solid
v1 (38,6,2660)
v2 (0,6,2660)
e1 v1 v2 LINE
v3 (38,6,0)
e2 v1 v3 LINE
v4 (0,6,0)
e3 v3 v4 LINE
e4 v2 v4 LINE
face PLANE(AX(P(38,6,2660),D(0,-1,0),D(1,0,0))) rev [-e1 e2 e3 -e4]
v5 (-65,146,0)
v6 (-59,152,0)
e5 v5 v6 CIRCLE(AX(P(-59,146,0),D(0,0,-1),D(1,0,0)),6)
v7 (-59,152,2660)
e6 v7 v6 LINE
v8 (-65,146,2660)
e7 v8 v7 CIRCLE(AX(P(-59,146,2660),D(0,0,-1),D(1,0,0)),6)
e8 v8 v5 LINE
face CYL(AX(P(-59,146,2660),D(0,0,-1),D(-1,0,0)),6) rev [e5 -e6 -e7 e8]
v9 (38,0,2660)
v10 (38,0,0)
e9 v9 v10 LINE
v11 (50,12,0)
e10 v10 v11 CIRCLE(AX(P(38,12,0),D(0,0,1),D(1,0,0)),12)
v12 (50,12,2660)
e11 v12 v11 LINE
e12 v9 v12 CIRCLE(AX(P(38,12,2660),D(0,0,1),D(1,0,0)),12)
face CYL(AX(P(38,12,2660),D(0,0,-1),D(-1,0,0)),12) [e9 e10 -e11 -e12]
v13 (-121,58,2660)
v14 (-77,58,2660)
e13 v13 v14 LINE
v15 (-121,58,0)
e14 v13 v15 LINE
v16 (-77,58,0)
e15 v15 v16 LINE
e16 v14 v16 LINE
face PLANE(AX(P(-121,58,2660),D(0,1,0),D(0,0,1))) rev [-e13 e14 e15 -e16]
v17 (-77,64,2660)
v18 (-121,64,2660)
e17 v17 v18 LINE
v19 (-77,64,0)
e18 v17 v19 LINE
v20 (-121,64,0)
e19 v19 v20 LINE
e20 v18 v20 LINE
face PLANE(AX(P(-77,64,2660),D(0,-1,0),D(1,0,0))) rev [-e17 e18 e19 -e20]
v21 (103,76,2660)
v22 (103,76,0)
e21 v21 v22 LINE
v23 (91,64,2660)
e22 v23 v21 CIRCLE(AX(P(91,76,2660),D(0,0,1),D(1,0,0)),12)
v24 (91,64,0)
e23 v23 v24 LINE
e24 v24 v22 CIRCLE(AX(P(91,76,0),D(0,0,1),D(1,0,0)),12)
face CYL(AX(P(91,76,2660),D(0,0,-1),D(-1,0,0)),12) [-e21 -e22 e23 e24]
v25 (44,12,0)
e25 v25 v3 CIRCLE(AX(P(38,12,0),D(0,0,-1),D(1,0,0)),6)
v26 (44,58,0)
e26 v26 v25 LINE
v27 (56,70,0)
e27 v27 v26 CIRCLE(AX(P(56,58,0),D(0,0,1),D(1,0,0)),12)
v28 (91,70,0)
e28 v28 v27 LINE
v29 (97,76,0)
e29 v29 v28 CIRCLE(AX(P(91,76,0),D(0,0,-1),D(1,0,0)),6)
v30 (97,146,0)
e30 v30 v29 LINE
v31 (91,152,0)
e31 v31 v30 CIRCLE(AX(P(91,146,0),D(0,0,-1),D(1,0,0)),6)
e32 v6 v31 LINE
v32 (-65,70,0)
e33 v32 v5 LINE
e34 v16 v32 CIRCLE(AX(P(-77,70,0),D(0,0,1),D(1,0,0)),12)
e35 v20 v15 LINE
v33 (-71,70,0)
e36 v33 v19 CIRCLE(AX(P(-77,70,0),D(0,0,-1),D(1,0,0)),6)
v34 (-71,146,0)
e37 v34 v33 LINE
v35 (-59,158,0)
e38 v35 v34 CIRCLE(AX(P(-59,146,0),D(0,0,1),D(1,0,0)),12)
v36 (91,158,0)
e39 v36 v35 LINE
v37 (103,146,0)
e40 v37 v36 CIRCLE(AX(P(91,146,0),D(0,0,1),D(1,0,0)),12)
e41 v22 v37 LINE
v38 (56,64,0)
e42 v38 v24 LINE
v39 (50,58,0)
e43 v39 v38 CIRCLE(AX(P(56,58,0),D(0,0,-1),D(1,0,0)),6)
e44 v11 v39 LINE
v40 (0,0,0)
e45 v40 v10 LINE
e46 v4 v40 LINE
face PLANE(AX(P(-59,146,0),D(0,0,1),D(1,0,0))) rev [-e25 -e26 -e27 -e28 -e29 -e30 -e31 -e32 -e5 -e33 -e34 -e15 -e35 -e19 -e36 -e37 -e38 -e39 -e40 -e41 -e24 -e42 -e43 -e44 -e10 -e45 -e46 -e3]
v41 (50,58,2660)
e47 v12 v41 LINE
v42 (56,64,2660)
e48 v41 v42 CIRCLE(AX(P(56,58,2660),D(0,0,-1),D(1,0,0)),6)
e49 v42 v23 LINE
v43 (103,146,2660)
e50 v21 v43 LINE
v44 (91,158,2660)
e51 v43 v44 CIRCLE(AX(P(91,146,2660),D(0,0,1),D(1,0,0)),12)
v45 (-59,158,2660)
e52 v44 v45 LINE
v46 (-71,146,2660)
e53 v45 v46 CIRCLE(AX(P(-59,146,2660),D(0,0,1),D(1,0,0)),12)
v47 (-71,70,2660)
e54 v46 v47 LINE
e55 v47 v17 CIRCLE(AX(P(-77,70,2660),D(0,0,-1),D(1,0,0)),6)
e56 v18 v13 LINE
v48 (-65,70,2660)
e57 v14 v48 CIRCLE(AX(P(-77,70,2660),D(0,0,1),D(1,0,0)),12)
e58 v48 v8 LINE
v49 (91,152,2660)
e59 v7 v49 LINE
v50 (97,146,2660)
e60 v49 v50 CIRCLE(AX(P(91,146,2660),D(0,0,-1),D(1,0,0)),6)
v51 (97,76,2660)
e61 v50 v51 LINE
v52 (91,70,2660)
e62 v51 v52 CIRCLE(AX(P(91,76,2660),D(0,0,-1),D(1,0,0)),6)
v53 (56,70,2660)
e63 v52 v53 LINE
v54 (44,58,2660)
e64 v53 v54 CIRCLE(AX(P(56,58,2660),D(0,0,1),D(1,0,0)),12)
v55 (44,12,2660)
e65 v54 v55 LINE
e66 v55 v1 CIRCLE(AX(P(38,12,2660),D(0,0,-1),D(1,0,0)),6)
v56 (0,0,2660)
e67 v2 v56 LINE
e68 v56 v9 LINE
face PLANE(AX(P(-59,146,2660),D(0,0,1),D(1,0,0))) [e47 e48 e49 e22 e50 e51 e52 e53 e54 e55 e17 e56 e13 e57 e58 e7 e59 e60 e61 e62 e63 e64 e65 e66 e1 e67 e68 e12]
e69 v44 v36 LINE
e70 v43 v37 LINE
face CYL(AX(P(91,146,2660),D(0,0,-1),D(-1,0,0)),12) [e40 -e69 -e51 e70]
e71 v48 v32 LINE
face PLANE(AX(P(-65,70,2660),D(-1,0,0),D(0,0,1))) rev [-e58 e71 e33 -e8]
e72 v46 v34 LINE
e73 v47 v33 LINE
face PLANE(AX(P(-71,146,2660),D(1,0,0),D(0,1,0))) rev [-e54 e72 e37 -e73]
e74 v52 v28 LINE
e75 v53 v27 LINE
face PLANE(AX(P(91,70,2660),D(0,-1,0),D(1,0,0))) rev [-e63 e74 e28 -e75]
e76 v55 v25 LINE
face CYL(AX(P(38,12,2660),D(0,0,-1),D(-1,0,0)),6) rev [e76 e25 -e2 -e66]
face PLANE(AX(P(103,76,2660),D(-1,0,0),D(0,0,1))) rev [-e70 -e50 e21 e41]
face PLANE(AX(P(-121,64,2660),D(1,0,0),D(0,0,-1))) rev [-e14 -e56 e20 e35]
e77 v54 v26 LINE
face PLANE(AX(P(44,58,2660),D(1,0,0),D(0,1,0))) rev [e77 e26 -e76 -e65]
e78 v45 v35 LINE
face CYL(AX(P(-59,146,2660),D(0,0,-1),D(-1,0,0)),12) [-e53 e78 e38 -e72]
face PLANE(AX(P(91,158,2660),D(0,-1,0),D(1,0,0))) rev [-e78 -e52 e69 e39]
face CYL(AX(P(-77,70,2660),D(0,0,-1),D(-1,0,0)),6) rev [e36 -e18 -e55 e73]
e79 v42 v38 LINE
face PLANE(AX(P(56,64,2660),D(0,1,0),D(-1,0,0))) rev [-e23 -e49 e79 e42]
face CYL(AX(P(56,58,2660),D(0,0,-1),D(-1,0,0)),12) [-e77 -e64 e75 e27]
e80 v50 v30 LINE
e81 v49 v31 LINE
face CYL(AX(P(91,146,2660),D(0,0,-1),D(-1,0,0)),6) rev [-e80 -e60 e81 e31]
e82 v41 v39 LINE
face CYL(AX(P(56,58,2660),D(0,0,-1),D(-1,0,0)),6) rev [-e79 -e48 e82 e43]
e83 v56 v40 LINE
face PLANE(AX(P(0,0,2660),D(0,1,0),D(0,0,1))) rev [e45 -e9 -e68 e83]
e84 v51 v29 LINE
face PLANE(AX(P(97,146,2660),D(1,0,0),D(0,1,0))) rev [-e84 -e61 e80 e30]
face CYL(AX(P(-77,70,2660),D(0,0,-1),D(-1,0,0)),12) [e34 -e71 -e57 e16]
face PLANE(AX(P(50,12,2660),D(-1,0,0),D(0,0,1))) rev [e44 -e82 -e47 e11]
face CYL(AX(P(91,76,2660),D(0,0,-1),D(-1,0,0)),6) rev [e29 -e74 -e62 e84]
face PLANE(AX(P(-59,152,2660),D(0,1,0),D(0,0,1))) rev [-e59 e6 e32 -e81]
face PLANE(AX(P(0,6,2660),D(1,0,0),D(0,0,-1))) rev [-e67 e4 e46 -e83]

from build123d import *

# Parameters (mm, degrees)
BOSS_EXTRUDE1_DEPTH = 2660


with BuildPart() as part:
    # Sketch1 → Boss-Extrude1 (new body)
    with BuildSketch(Plane.XY):
        with BuildLine():
            Line((-70.999999998, 146), (-70.999999998, 70))
            ThreePointArc((-70.999999998, 70), (-72.757359311, 65.757359313), (-76.999999998, 64))
            Line((-76.999999998, 64), (-120.999999998, 64))
            Line((-120.999999998, 64), (-120.999999998, 58))
            Line((-120.999999998, 58), (-76.999999998, 58))
            ThreePointArc((-76.999999998, 58), (-68.514718624, 61.514718626), (-64.999999998, 70))
            Line((-64.999999998, 70), (-64.999999998, 146))
            ThreePointArc((-64.999999998, 146), (-63.242640685, 150.242640687), (-58.999999998, 152))
            Line((-58.999999998, 152), (91, 152))
            ThreePointArc((91, 152), (95.242640687, 150.242640687), (97, 146))
            Line((97, 146), (97, 76))
            ThreePointArc((97, 76), (95.242640687, 71.757359313), (91, 70))
            Line((91, 70), (56, 70))
            ThreePointArc((56, 70), (47.514718626, 66.485281374), (44, 58))
            Line((44, 58), (44, 12))
            ThreePointArc((44, 12), (42.242640687, 7.757359313), (38, 6))
            Line((38, 6), (0, 6))
            Line((0, 6), (0, 0))
            Line((0, 0), (38, 0))
            ThreePointArc((38, 0), (46.485281374, 3.514718626), (50, 12))
            Line((50, 12), (50, 58))
            ThreePointArc((50, 58), (51.757359313, 62.242640687), (56, 64))
            Line((56, 64), (91, 64))
            ThreePointArc((91, 64), (99.485281374, 67.514718626), (103, 76))
            Line((103, 76), (103, 146))
            ThreePointArc((103, 146), (99.485281374, 154.485281374), (91, 158))
            Line((91, 158), (-58.999999998, 158))
            ThreePointArc((-58.999999998, 158), (-67.485281372, 154.485281374), (-70.999999998, 146))
        make_face()
    extrude(amount=BOSS_EXTRUDE1_DEPTH)


solid = part.part
